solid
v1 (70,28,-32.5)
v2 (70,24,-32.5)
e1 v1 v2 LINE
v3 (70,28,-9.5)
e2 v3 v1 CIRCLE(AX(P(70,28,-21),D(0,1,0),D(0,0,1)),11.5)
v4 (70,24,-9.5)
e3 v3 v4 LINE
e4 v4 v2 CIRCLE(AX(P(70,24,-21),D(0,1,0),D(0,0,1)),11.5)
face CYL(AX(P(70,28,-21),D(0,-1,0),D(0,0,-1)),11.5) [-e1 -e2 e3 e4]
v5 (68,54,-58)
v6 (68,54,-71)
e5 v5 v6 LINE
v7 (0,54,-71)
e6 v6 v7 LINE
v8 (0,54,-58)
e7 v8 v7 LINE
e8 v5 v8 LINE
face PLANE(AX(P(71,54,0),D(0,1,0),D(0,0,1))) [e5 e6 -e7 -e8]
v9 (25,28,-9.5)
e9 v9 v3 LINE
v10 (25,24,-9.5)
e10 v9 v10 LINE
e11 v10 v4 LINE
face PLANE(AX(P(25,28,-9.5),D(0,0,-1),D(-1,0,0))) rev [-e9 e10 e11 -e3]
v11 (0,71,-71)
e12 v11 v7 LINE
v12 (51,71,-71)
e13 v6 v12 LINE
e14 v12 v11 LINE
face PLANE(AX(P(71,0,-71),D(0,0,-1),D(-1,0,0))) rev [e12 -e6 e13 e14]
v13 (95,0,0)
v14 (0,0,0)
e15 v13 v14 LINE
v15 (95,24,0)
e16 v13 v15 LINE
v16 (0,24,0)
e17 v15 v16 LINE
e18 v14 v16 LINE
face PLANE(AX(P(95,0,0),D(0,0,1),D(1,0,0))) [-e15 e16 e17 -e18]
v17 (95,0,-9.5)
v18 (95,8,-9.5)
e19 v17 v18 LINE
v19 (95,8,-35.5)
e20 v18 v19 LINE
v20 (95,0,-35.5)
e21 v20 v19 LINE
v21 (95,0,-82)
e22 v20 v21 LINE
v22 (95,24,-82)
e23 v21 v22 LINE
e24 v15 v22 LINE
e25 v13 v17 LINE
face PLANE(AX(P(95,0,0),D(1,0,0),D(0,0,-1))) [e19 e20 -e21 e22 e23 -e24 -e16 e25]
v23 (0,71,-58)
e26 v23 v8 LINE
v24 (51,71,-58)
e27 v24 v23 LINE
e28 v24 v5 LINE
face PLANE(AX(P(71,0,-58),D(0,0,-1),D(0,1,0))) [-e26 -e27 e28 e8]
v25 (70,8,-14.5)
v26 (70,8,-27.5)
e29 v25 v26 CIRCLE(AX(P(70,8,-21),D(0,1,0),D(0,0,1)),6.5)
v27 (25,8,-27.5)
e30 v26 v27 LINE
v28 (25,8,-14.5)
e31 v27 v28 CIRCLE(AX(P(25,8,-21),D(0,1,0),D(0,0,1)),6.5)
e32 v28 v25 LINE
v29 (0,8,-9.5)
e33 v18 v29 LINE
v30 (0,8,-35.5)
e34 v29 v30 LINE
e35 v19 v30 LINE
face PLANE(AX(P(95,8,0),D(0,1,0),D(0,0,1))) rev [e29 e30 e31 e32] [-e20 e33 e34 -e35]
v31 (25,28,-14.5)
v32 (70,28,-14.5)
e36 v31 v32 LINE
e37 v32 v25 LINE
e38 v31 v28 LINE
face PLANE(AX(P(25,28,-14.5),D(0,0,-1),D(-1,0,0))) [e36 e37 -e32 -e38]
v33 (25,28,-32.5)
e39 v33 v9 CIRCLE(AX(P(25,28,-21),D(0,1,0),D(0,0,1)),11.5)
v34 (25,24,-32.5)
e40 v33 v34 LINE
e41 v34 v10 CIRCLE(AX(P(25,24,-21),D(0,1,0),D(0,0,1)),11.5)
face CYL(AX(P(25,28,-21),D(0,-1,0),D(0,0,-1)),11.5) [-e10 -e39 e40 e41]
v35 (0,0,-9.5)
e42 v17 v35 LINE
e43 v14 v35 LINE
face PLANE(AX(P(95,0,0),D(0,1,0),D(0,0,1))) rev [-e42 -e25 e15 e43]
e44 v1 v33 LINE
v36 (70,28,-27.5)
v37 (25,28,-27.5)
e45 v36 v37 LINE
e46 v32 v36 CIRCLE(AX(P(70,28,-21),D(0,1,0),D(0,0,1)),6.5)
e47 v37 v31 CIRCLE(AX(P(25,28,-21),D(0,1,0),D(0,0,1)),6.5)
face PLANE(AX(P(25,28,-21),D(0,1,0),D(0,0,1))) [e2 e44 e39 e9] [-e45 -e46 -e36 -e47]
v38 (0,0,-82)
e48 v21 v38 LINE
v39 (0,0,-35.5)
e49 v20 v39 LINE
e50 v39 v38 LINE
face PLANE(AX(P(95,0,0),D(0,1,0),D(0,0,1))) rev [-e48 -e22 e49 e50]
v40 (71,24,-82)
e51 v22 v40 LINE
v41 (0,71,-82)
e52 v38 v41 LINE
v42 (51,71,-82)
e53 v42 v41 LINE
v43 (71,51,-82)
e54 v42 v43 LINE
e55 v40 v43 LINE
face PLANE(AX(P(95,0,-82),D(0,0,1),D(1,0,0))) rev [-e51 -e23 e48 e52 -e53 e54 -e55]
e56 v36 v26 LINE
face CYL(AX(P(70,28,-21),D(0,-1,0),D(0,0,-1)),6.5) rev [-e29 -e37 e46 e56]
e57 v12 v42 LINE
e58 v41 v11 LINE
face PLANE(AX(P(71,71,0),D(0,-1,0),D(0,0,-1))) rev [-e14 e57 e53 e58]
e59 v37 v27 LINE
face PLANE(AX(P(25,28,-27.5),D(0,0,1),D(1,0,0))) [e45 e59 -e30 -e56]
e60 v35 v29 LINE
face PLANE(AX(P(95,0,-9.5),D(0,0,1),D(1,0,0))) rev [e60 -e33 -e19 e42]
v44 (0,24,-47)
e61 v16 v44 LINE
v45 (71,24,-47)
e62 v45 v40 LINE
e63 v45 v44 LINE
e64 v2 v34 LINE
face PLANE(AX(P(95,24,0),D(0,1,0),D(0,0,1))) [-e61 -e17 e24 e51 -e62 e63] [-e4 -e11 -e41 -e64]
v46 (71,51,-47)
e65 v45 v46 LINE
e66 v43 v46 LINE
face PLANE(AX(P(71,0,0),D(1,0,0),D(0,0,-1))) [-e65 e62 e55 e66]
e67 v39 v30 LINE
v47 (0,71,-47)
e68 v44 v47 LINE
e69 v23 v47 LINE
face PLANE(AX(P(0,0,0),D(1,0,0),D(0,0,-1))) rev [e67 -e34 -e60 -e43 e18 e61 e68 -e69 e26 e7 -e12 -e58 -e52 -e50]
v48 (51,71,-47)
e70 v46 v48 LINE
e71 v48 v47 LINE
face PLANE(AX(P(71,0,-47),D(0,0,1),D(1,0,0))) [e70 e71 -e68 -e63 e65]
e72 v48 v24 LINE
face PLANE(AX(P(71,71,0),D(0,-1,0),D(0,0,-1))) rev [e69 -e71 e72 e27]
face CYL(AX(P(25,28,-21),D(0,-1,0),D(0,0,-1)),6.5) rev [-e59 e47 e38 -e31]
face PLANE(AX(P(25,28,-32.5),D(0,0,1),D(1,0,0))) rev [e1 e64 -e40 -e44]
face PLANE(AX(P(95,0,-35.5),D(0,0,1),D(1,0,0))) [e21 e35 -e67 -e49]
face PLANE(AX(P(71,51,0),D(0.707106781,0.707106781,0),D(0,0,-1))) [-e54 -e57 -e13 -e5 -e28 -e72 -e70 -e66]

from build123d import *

# Parameters (mm, degrees)
BASE_BLOCK_DEPTH           = 95
UPRIGHT_BLOCK_DEPTH        = 71
UPRIGHT_CHAMFER_20X45_SIZE = 20
SLOT_RIM_BOSS_DEPTH        = 4
THROUGH_START              = -154
THROUGH_SLOT_CUT_DEPTH     = 154


with BuildPart() as part:
    # Base and Upright Profile Sketch → Base Block (new body)
    with BuildSketch(Plane(origin=(0, 0, 0), x_dir=(0, 0, -1), z_dir=(1, 0, 0))):
        Polygon((35.5, 0), (35.5, 8), (9.5, 8), (9.5, 0), (0, 0), (0, 24), (82, 24), (82, 0), align=None)
    extrude(amount=BASE_BLOCK_DEPTH)

    # Sketch1_3 → Upright Block (add)
    with BuildSketch(Plane(origin=(0, 0, 0), x_dir=(0, 0, -1), z_dir=(1, 0, 0))):
        Polygon((58, 54), (58, 71), (47, 71), (47, 24), (82, 24), (82, 71), (71, 71), (71, 54), align=None)
    extrude(amount=UPRIGHT_BLOCK_DEPTH)

    # Upright Chamfer 20x45
    upright_chamfer_20x45_edges = [part.edges().sort_by_distance(p)[0] for p in [
        (71, 71, -52.5),
    ]]
    chamfer(upright_chamfer_20x45_edges, length=UPRIGHT_CHAMFER_20X45_SIZE)

    # Slot Rim Sketch → Slot Rim Boss (add)
    with BuildSketch(Plane(origin=(0, 24, 0), x_dir=(1, 0, 0), z_dir=(0, 1, 0))):
        with BuildLine():
            Line((25, 32.5), (70, 32.5))
            ThreePointArc((70, 32.5), (81.5, 21), (70, 9.5))
            Line((70, 9.5), (25, 9.5))
            ThreePointArc((25, 9.5), (13.5, 21), (25, 32.5))
        make_face()
        with BuildLine():
            Line((25, 27.5), (70, 27.5))
            ThreePointArc((70, 27.5), (76.5, 21), (70, 14.5))
            Line((70, 14.5), (25, 14.5))
            ThreePointArc((25, 14.5), (18.5, 21), (25, 27.5))
        make_face(mode=Mode.SUBTRACT)
    extrude(amount=SLOT_RIM_BOSS_DEPTH)

    # Through Slot Sketch → Through Slot Cut (cut)
    with BuildSketch(Plane(origin=(0, 24, 0), x_dir=(1, 0, 0), z_dir=(0, 1, 0)).offset(THROUGH_START)):
        with BuildLine():
            Line((25, 27.5), (70, 27.5))
            ThreePointArc((70, 27.5), (76.5, 21), (70, 14.5))
            Line((70, 14.5), (25, 14.5))
            ThreePointArc((25, 14.5), (18.5, 21), (25, 27.5))
        make_face()
    extrude(amount=THROUGH_SLOT_CUT_DEPTH, mode=Mode.SUBTRACT)


solid = part.part
